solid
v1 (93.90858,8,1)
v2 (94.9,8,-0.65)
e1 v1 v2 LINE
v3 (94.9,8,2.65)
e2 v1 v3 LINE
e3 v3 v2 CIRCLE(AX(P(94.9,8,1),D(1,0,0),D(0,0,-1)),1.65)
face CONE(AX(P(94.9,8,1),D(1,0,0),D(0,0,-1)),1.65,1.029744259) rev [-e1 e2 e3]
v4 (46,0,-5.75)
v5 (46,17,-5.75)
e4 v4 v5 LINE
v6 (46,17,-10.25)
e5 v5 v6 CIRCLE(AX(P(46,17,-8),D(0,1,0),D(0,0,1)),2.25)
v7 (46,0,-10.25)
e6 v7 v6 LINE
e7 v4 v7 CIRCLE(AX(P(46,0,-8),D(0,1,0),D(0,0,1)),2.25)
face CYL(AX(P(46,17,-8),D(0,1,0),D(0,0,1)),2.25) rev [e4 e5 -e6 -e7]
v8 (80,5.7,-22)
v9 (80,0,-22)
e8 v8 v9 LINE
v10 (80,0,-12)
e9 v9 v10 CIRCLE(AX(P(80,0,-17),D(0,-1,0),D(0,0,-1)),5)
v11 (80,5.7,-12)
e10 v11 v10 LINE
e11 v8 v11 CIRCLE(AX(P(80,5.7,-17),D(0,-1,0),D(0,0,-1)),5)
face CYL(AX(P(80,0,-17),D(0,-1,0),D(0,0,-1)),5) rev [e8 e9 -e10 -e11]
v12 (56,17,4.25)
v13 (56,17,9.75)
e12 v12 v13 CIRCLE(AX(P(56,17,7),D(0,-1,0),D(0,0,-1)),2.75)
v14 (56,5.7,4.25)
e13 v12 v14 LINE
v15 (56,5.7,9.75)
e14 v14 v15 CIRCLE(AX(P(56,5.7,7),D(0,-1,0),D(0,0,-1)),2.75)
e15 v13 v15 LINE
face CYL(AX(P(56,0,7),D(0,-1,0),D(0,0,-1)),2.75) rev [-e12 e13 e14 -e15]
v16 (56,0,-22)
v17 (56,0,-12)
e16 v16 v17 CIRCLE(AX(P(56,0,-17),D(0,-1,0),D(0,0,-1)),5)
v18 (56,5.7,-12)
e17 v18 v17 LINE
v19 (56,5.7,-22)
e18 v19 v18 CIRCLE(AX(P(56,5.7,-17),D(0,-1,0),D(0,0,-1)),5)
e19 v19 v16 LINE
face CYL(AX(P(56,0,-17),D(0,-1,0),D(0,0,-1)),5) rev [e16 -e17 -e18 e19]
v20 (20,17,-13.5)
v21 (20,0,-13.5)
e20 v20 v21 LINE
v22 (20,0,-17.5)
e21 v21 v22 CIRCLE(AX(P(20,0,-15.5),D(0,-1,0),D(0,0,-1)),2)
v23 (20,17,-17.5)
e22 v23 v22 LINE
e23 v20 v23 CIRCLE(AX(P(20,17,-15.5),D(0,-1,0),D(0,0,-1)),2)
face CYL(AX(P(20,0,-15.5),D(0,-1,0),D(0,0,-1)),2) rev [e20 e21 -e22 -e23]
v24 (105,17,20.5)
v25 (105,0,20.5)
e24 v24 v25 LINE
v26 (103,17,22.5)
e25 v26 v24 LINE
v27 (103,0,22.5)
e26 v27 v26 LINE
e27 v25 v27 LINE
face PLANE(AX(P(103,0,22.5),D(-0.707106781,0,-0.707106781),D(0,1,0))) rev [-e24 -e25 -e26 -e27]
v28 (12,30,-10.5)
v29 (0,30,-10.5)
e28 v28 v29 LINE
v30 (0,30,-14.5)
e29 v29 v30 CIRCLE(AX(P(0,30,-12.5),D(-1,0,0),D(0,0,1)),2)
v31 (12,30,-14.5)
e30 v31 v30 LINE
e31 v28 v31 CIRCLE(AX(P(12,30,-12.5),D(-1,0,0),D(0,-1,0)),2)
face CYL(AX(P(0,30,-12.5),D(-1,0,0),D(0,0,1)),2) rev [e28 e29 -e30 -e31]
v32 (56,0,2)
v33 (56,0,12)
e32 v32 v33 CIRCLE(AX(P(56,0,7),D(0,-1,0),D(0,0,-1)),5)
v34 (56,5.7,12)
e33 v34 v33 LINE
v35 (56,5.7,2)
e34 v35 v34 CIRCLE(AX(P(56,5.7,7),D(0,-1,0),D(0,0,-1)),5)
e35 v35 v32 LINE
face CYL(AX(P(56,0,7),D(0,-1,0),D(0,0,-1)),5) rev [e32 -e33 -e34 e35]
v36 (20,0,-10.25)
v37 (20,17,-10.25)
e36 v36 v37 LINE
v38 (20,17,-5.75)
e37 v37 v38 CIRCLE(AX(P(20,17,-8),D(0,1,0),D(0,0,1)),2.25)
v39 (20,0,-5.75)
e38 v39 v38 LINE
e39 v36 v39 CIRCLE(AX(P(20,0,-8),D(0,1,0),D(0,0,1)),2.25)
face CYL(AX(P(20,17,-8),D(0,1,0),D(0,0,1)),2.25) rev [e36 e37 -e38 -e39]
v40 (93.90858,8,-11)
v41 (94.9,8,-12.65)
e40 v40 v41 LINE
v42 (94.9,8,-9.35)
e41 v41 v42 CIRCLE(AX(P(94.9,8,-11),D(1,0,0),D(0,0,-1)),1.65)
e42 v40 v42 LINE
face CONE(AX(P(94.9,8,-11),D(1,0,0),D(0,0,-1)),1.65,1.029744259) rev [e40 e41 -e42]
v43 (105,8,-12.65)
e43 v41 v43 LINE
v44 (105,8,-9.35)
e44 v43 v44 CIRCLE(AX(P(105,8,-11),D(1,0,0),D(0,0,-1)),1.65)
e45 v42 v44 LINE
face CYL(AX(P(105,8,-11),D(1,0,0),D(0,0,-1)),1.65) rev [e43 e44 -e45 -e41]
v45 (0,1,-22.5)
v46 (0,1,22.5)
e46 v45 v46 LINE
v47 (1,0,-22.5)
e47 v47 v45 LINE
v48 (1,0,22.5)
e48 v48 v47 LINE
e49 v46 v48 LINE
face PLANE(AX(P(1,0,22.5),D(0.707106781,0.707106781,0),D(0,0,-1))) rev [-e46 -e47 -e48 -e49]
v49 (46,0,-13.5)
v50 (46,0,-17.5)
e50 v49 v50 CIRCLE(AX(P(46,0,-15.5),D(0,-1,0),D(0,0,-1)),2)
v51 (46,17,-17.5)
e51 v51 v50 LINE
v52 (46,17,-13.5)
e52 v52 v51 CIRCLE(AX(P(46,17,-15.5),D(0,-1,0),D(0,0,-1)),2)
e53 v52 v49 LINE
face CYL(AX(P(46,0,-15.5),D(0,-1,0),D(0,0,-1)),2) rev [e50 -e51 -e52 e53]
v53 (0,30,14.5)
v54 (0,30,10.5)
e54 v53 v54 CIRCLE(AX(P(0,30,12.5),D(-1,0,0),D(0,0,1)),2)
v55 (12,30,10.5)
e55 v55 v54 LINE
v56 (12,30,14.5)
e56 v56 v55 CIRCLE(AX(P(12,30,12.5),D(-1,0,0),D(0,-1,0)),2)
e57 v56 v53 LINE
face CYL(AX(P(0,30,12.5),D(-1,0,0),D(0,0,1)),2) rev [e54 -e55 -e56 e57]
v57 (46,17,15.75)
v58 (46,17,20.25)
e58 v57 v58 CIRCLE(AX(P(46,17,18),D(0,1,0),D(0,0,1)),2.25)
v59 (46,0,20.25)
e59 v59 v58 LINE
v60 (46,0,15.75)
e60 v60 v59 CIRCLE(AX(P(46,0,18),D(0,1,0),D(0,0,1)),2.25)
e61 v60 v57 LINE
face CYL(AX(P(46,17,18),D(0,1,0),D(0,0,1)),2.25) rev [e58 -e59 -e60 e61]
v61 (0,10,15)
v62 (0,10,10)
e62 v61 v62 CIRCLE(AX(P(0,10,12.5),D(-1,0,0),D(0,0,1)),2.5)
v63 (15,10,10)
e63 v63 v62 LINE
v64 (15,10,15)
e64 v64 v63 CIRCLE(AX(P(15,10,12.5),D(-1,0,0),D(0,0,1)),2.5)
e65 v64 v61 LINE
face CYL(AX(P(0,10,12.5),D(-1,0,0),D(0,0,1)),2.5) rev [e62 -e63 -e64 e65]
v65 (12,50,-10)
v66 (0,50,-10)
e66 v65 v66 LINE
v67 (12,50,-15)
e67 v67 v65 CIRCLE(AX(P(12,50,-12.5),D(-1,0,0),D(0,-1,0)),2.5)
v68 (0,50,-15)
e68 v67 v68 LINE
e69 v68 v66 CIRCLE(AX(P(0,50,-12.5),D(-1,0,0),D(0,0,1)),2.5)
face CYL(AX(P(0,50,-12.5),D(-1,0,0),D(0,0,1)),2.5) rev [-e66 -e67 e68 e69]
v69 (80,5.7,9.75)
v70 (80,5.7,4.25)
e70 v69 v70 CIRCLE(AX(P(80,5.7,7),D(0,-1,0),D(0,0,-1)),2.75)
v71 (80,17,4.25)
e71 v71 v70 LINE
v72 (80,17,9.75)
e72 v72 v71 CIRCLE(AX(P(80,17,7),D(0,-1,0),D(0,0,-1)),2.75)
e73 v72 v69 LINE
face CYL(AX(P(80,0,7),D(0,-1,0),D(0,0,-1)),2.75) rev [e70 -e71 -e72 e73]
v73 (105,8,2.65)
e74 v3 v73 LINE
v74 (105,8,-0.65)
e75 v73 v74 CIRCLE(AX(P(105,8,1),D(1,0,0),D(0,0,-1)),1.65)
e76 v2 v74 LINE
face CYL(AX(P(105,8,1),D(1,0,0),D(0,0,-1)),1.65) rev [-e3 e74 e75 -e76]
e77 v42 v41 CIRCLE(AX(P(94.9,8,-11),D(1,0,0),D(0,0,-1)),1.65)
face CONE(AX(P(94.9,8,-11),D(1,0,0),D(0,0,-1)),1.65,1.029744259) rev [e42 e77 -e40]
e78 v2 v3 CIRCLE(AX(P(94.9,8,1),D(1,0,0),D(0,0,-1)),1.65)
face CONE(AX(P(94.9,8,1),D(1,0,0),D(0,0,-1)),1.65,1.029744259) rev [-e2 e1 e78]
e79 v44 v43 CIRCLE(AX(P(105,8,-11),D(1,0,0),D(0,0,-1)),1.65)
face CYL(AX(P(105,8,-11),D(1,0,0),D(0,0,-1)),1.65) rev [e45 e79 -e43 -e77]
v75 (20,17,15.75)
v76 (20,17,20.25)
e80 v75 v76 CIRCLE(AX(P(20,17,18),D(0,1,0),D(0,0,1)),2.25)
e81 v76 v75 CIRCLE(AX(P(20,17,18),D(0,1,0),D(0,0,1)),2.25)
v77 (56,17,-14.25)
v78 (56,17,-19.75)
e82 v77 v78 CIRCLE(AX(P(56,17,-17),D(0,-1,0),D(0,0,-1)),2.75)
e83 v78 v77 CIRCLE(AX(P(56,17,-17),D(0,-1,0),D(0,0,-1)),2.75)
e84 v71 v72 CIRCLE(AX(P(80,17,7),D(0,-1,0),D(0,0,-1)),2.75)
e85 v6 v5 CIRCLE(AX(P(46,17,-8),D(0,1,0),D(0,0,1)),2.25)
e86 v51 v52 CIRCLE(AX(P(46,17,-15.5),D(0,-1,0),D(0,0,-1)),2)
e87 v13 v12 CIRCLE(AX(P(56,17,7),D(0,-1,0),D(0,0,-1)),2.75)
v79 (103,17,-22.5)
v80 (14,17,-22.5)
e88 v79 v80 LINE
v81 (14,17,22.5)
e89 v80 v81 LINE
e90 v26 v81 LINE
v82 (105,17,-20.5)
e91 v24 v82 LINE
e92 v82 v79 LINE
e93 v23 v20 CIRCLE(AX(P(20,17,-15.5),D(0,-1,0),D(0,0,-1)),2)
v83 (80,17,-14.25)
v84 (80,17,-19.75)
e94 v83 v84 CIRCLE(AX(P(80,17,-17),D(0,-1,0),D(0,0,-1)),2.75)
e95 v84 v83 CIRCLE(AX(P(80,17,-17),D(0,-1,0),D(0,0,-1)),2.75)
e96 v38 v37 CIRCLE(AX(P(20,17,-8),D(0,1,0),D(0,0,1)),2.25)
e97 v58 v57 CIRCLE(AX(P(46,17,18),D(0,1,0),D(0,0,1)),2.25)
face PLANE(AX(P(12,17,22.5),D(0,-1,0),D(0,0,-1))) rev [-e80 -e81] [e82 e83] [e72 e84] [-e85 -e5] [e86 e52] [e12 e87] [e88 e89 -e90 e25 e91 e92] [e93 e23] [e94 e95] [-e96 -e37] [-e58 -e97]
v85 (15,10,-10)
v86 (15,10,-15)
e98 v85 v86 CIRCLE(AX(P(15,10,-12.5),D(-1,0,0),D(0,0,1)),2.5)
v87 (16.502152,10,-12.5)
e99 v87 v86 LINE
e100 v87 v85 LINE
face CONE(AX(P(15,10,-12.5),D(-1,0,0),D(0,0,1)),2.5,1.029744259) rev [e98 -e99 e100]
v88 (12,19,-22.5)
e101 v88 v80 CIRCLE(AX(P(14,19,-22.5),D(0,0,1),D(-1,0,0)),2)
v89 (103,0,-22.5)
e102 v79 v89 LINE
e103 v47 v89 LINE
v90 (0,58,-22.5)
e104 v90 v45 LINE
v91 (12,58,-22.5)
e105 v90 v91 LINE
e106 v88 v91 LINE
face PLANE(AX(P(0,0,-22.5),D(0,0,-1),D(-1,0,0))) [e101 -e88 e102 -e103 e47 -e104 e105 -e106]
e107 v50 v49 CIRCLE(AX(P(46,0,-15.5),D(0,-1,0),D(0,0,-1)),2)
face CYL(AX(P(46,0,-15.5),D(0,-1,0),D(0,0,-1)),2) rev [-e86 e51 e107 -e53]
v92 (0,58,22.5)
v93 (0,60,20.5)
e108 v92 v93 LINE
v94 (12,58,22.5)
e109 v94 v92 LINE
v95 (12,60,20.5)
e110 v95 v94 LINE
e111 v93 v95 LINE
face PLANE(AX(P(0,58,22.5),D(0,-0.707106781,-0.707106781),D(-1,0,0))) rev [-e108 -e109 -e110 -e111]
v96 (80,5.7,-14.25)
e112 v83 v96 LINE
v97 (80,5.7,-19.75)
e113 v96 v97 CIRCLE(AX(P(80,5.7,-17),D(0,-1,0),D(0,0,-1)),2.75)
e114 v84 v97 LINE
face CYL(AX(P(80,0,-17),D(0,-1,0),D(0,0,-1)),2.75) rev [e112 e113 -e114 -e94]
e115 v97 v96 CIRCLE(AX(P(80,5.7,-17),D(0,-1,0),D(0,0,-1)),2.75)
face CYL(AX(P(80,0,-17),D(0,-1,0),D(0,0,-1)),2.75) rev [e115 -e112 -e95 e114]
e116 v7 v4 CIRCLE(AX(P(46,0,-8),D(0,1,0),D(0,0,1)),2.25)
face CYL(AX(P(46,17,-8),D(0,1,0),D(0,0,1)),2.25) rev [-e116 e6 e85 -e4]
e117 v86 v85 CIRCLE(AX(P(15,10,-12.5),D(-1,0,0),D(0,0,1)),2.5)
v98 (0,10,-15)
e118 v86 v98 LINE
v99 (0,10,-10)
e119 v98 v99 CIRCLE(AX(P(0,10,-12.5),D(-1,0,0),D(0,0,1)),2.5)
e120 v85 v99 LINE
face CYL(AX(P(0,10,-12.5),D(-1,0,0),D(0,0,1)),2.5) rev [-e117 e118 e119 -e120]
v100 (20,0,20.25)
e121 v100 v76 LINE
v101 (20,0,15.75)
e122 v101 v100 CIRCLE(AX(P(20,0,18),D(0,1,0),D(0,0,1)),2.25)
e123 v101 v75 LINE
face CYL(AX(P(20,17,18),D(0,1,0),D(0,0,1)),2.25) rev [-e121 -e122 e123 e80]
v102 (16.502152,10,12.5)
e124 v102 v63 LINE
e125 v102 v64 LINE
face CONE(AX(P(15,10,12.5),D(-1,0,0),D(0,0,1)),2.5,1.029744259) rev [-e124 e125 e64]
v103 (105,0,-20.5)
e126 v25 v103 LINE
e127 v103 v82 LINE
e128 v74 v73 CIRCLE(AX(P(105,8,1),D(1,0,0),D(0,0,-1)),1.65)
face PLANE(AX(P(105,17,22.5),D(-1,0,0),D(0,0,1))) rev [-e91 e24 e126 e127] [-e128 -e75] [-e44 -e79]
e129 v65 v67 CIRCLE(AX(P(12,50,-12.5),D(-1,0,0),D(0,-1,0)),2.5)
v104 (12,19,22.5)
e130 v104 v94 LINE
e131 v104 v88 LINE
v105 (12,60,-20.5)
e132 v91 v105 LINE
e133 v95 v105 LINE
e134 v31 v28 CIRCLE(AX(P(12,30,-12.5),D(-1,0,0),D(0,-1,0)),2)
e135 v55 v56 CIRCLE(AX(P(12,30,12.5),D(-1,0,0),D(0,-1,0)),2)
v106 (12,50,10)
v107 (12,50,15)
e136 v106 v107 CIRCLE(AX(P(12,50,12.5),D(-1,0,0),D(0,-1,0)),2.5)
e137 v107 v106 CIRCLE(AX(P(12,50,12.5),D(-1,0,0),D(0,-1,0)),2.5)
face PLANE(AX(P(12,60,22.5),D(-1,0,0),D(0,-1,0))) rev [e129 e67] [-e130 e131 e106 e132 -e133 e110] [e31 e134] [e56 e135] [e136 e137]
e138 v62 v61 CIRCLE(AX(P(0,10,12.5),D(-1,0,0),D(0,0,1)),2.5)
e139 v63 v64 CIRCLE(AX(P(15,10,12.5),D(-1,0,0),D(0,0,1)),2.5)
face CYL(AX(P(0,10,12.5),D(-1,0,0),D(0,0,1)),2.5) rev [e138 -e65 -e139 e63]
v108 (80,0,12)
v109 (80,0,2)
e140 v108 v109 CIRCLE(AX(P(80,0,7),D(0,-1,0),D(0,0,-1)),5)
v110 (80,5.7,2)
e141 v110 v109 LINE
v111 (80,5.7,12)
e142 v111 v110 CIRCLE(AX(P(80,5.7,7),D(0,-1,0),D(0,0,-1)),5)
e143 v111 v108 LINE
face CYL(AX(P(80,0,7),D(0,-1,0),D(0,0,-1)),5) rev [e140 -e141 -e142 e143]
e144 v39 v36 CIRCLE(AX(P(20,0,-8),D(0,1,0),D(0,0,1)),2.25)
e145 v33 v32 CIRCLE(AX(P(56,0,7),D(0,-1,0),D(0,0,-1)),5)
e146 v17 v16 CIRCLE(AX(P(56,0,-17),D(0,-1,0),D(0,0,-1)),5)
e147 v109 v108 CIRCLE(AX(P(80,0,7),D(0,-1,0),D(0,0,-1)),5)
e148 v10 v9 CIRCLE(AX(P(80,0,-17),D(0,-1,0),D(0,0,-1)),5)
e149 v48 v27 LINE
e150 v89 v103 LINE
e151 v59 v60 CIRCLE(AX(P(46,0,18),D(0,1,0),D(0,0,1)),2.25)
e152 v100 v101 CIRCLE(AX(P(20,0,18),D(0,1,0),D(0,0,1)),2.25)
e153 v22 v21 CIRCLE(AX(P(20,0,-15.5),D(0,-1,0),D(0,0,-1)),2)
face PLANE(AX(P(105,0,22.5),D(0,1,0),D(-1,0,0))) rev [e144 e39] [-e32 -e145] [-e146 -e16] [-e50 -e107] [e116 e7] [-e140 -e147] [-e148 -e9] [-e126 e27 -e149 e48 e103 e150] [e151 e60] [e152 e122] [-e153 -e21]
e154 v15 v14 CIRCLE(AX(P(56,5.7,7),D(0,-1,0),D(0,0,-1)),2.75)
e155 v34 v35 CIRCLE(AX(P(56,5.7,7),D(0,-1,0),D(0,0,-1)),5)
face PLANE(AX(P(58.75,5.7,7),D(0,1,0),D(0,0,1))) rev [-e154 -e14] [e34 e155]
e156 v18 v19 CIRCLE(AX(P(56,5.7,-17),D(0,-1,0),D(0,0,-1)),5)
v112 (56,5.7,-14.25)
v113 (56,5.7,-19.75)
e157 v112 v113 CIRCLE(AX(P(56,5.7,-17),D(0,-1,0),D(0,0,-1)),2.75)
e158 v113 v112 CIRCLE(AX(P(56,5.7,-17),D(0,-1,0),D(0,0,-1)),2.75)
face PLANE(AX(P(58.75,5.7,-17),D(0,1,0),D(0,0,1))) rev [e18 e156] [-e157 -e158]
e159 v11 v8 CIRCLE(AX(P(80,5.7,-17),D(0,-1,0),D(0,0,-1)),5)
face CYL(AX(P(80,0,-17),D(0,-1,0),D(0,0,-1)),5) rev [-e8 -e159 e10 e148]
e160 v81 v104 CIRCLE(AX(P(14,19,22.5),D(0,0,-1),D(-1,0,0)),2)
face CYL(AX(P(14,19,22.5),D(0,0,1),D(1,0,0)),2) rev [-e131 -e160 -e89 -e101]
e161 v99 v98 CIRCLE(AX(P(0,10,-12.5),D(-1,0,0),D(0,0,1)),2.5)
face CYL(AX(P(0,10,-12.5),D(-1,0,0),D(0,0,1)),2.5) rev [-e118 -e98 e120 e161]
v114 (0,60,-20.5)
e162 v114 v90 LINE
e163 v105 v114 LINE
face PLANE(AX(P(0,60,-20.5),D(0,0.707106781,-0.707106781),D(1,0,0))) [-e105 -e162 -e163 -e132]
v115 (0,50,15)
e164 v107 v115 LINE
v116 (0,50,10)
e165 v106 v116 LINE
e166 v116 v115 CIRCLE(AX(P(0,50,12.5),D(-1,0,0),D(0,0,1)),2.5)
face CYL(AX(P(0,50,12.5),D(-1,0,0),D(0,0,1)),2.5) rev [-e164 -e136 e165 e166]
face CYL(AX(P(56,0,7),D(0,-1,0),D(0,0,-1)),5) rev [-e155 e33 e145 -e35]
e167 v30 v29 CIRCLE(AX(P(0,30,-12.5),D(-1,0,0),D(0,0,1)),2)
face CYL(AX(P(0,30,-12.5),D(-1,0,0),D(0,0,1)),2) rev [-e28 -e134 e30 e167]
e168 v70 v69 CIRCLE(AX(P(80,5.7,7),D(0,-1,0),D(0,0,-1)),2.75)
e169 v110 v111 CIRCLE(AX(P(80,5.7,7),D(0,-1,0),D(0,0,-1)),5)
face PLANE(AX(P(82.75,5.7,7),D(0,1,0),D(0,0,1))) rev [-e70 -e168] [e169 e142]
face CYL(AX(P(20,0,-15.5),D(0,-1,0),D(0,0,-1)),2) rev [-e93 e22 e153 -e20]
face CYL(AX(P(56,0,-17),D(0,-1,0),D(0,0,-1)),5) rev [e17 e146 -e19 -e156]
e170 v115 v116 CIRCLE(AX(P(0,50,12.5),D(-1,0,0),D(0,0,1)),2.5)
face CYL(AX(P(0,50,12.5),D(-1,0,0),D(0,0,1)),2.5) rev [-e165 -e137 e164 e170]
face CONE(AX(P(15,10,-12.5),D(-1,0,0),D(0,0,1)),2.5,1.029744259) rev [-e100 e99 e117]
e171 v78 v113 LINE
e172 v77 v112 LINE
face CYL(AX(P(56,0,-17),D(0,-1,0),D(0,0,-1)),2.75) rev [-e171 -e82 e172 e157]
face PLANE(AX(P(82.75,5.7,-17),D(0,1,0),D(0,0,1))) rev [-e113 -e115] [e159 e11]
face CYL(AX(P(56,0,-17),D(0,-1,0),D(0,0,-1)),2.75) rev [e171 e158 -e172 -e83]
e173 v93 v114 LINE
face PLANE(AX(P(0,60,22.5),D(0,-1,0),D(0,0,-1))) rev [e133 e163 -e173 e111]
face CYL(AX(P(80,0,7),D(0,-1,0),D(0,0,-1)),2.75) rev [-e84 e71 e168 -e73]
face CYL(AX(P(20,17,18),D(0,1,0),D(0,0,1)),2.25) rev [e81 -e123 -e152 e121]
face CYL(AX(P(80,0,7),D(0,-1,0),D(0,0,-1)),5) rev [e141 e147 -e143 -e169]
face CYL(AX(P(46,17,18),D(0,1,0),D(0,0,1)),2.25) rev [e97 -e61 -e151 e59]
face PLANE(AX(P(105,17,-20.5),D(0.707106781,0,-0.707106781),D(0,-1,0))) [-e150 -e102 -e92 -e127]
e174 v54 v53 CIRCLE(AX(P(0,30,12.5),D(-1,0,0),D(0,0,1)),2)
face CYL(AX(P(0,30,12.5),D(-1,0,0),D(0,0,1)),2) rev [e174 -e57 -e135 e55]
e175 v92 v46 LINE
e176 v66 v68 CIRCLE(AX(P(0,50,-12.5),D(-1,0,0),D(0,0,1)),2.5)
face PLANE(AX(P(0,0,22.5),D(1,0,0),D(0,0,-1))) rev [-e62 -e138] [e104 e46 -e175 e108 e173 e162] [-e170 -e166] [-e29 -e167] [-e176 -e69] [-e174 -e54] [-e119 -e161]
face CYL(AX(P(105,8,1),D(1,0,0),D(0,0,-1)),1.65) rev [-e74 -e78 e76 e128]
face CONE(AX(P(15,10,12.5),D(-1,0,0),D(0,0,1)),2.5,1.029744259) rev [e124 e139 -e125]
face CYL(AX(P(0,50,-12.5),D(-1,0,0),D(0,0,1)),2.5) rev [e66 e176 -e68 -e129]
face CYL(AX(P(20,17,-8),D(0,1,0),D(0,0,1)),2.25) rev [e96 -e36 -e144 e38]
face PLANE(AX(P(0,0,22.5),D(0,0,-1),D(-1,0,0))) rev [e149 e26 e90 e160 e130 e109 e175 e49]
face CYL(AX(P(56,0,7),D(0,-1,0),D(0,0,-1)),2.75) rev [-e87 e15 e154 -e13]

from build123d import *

# Parameters (mm, degrees)
BOSS_EXTRUDE1_DEPTH                                  = 22.5
HOLE_SIZE_PER_SOCKET_HEAD_CAP_SCREW_TYPE_D           = 5.5
HOLE_SIZE_PER_SOCKET_HEAD_CAP_SCREW_TYPE_CBORE_D     = 10
HOLE_SIZE_PER_SOCKET_HEAD_CAP_SCREW_TYPE_CBORE_DEPTH = 5.7
F_4_5_4_5_DIAMETER_HOLE1_D                           = 4.5
M4_TAPPED_HOLE1_D                                    = 3.3
M4_TAPPED_HOLE1_DEPTH                                = 10.1
M4_TAPPED_HOLE1_TIP                                  = 0.991420021
M6_TAPPED_HOLE1_D                                    = 5
M6_TAPPED_HOLE1_DEPTH                                = 15
M6_TAPPED_HOLE1_TIP                                  = 1.502151548
F_4_0_4_DIAMETER_HOLE1_D                             = 4
F_4_0_4_DIAMETER_HOLE1_DEPTH                         = 15
F_4_0_4_DIAMETER_HOLE1_TIP                           = 1.201721238
F_4_0_4_DIAMETER_HOLE2_D                             = 4
F_4_0_4_DIAMETER_HOLE2_DEPTH                         = 17
F_4_0_4_DIAMETER_HOLE2_TIP                           = 1.201721238
CHAMFER1_SIZE                                        = 2
CHAMFER2_SIZE                                        = 1
FILLET1_R                                            = 2


with BuildPart() as part:
    # Sketch1 → Boss-Extrude1 (new, symmetric)
    with BuildSketch(Plane.XY):
        Polygon((0, 0), (0, 60), (12, 60), (12, 17), (105, 17), (105, 0), align=None)
    extrude(amount=BOSS_EXTRUDE1_DEPTH, both=True)

    # Hole size per socket head cap screw type 1 (through all)
    with Locations(Plane(origin=(0, 0, 0), x_dir=(-1, 0, 0), z_dir=(0, -1, 0))):
        with Locations((-80, -7), (-56, -7), (-56, 17), (-80, 17)):
            CounterBoreHole(HOLE_SIZE_PER_SOCKET_HEAD_CAP_SCREW_TYPE_D / 2, HOLE_SIZE_PER_SOCKET_HEAD_CAP_SCREW_TYPE_CBORE_D / 2, HOLE_SIZE_PER_SOCKET_HEAD_CAP_SCREW_TYPE_CBORE_DEPTH)

    # Ø4.5 (4.5) Diameter Hole1 (through all)
    with Locations(Plane(origin=(0, 17, 0), x_dir=(1, 0, 0), z_dir=(0, 1, 0))):
        with Locations((20, 8), (46, 8), (20, -18), (46, -18)):
            Hole(F_4_5_4_5_DIAMETER_HOLE1_D / 2)

    # M4 Tapped Hole1
    with Locations(Plane(origin=(105, 0, 0), x_dir=(0, 0, -1), z_dir=(1, 0, 0))):
        with Locations((-1, 8), (11, 8)):
            Hole(M4_TAPPED_HOLE1_D / 2, depth=M4_TAPPED_HOLE1_DEPTH)
            with Locations((0, 0, -(M4_TAPPED_HOLE1_DEPTH + M4_TAPPED_HOLE1_TIP / 2))):  # 118° drill point
                Cone(0, M4_TAPPED_HOLE1_D / 2, M4_TAPPED_HOLE1_TIP, mode=Mode.SUBTRACT)

    # M6 Tapped Hole1
    with Locations(Plane.ZY):
        with Locations((-12.5, 50), (12.5, 50), (-12.5, 10), (12.5, 10)):
            Hole(M6_TAPPED_HOLE1_D / 2, depth=M6_TAPPED_HOLE1_DEPTH)
            with Locations((0, 0, -(M6_TAPPED_HOLE1_DEPTH + M6_TAPPED_HOLE1_TIP / 2))):  # 118° drill point
                Cone(0, M6_TAPPED_HOLE1_D / 2, M6_TAPPED_HOLE1_TIP, mode=Mode.SUBTRACT)

    # Ø4.0 (4) Diameter Hole1
    with Locations(Plane.ZY):
        with Locations((-12.5, 30), (12.5, 30)):
            Hole(F_4_0_4_DIAMETER_HOLE1_D / 2, depth=F_4_0_4_DIAMETER_HOLE1_DEPTH)
            with Locations((0, 0, -(F_4_0_4_DIAMETER_HOLE1_DEPTH + F_4_0_4_DIAMETER_HOLE1_TIP / 2))):  # 118° drill point
                Cone(0, F_4_0_4_DIAMETER_HOLE1_D / 2, F_4_0_4_DIAMETER_HOLE1_TIP, mode=Mode.SUBTRACT)

    # Ø4.0 (4) Diameter Hole2
    with Locations(Plane(origin=(0, 0, 0), x_dir=(-1, 0, 0), z_dir=(0, -1, 0))):
        with Locations((-20, 15.5), (-46, 15.5)):
            Hole(F_4_0_4_DIAMETER_HOLE2_D / 2, depth=F_4_0_4_DIAMETER_HOLE2_DEPTH)
            with Locations((0, 0, -(F_4_0_4_DIAMETER_HOLE2_DEPTH + F_4_0_4_DIAMETER_HOLE2_TIP / 2))):  # 118° drill point
                Cone(0, F_4_0_4_DIAMETER_HOLE2_D / 2, F_4_0_4_DIAMETER_HOLE2_TIP, mode=Mode.SUBTRACT)

    # Chamfer1
    chamfer1_edges = [part.edges().sort_by_distance(p)[0] for p in [
        (6, 60, 22.5),
        (6, 60, -22.5),
        (105, 8.5, 22.5),
        (105, 8.5, -22.5),
    ]]
    chamfer(chamfer1_edges, length=CHAMFER1_SIZE)

    # Chamfer2
    chamfer2_edges = [part.edges().sort_by_distance(p)[0] for p in [
        (0, 0, 0),
    ]]
    chamfer(chamfer2_edges, length=CHAMFER2_SIZE)

    # Fillet1
    fillet1_edges = [part.edges().sort_by_distance(p)[0] for p in [
        (12, 17, 0),
    ]]
    fillet(fillet1_edges, radius=FILLET1_R)


solid = part.part
